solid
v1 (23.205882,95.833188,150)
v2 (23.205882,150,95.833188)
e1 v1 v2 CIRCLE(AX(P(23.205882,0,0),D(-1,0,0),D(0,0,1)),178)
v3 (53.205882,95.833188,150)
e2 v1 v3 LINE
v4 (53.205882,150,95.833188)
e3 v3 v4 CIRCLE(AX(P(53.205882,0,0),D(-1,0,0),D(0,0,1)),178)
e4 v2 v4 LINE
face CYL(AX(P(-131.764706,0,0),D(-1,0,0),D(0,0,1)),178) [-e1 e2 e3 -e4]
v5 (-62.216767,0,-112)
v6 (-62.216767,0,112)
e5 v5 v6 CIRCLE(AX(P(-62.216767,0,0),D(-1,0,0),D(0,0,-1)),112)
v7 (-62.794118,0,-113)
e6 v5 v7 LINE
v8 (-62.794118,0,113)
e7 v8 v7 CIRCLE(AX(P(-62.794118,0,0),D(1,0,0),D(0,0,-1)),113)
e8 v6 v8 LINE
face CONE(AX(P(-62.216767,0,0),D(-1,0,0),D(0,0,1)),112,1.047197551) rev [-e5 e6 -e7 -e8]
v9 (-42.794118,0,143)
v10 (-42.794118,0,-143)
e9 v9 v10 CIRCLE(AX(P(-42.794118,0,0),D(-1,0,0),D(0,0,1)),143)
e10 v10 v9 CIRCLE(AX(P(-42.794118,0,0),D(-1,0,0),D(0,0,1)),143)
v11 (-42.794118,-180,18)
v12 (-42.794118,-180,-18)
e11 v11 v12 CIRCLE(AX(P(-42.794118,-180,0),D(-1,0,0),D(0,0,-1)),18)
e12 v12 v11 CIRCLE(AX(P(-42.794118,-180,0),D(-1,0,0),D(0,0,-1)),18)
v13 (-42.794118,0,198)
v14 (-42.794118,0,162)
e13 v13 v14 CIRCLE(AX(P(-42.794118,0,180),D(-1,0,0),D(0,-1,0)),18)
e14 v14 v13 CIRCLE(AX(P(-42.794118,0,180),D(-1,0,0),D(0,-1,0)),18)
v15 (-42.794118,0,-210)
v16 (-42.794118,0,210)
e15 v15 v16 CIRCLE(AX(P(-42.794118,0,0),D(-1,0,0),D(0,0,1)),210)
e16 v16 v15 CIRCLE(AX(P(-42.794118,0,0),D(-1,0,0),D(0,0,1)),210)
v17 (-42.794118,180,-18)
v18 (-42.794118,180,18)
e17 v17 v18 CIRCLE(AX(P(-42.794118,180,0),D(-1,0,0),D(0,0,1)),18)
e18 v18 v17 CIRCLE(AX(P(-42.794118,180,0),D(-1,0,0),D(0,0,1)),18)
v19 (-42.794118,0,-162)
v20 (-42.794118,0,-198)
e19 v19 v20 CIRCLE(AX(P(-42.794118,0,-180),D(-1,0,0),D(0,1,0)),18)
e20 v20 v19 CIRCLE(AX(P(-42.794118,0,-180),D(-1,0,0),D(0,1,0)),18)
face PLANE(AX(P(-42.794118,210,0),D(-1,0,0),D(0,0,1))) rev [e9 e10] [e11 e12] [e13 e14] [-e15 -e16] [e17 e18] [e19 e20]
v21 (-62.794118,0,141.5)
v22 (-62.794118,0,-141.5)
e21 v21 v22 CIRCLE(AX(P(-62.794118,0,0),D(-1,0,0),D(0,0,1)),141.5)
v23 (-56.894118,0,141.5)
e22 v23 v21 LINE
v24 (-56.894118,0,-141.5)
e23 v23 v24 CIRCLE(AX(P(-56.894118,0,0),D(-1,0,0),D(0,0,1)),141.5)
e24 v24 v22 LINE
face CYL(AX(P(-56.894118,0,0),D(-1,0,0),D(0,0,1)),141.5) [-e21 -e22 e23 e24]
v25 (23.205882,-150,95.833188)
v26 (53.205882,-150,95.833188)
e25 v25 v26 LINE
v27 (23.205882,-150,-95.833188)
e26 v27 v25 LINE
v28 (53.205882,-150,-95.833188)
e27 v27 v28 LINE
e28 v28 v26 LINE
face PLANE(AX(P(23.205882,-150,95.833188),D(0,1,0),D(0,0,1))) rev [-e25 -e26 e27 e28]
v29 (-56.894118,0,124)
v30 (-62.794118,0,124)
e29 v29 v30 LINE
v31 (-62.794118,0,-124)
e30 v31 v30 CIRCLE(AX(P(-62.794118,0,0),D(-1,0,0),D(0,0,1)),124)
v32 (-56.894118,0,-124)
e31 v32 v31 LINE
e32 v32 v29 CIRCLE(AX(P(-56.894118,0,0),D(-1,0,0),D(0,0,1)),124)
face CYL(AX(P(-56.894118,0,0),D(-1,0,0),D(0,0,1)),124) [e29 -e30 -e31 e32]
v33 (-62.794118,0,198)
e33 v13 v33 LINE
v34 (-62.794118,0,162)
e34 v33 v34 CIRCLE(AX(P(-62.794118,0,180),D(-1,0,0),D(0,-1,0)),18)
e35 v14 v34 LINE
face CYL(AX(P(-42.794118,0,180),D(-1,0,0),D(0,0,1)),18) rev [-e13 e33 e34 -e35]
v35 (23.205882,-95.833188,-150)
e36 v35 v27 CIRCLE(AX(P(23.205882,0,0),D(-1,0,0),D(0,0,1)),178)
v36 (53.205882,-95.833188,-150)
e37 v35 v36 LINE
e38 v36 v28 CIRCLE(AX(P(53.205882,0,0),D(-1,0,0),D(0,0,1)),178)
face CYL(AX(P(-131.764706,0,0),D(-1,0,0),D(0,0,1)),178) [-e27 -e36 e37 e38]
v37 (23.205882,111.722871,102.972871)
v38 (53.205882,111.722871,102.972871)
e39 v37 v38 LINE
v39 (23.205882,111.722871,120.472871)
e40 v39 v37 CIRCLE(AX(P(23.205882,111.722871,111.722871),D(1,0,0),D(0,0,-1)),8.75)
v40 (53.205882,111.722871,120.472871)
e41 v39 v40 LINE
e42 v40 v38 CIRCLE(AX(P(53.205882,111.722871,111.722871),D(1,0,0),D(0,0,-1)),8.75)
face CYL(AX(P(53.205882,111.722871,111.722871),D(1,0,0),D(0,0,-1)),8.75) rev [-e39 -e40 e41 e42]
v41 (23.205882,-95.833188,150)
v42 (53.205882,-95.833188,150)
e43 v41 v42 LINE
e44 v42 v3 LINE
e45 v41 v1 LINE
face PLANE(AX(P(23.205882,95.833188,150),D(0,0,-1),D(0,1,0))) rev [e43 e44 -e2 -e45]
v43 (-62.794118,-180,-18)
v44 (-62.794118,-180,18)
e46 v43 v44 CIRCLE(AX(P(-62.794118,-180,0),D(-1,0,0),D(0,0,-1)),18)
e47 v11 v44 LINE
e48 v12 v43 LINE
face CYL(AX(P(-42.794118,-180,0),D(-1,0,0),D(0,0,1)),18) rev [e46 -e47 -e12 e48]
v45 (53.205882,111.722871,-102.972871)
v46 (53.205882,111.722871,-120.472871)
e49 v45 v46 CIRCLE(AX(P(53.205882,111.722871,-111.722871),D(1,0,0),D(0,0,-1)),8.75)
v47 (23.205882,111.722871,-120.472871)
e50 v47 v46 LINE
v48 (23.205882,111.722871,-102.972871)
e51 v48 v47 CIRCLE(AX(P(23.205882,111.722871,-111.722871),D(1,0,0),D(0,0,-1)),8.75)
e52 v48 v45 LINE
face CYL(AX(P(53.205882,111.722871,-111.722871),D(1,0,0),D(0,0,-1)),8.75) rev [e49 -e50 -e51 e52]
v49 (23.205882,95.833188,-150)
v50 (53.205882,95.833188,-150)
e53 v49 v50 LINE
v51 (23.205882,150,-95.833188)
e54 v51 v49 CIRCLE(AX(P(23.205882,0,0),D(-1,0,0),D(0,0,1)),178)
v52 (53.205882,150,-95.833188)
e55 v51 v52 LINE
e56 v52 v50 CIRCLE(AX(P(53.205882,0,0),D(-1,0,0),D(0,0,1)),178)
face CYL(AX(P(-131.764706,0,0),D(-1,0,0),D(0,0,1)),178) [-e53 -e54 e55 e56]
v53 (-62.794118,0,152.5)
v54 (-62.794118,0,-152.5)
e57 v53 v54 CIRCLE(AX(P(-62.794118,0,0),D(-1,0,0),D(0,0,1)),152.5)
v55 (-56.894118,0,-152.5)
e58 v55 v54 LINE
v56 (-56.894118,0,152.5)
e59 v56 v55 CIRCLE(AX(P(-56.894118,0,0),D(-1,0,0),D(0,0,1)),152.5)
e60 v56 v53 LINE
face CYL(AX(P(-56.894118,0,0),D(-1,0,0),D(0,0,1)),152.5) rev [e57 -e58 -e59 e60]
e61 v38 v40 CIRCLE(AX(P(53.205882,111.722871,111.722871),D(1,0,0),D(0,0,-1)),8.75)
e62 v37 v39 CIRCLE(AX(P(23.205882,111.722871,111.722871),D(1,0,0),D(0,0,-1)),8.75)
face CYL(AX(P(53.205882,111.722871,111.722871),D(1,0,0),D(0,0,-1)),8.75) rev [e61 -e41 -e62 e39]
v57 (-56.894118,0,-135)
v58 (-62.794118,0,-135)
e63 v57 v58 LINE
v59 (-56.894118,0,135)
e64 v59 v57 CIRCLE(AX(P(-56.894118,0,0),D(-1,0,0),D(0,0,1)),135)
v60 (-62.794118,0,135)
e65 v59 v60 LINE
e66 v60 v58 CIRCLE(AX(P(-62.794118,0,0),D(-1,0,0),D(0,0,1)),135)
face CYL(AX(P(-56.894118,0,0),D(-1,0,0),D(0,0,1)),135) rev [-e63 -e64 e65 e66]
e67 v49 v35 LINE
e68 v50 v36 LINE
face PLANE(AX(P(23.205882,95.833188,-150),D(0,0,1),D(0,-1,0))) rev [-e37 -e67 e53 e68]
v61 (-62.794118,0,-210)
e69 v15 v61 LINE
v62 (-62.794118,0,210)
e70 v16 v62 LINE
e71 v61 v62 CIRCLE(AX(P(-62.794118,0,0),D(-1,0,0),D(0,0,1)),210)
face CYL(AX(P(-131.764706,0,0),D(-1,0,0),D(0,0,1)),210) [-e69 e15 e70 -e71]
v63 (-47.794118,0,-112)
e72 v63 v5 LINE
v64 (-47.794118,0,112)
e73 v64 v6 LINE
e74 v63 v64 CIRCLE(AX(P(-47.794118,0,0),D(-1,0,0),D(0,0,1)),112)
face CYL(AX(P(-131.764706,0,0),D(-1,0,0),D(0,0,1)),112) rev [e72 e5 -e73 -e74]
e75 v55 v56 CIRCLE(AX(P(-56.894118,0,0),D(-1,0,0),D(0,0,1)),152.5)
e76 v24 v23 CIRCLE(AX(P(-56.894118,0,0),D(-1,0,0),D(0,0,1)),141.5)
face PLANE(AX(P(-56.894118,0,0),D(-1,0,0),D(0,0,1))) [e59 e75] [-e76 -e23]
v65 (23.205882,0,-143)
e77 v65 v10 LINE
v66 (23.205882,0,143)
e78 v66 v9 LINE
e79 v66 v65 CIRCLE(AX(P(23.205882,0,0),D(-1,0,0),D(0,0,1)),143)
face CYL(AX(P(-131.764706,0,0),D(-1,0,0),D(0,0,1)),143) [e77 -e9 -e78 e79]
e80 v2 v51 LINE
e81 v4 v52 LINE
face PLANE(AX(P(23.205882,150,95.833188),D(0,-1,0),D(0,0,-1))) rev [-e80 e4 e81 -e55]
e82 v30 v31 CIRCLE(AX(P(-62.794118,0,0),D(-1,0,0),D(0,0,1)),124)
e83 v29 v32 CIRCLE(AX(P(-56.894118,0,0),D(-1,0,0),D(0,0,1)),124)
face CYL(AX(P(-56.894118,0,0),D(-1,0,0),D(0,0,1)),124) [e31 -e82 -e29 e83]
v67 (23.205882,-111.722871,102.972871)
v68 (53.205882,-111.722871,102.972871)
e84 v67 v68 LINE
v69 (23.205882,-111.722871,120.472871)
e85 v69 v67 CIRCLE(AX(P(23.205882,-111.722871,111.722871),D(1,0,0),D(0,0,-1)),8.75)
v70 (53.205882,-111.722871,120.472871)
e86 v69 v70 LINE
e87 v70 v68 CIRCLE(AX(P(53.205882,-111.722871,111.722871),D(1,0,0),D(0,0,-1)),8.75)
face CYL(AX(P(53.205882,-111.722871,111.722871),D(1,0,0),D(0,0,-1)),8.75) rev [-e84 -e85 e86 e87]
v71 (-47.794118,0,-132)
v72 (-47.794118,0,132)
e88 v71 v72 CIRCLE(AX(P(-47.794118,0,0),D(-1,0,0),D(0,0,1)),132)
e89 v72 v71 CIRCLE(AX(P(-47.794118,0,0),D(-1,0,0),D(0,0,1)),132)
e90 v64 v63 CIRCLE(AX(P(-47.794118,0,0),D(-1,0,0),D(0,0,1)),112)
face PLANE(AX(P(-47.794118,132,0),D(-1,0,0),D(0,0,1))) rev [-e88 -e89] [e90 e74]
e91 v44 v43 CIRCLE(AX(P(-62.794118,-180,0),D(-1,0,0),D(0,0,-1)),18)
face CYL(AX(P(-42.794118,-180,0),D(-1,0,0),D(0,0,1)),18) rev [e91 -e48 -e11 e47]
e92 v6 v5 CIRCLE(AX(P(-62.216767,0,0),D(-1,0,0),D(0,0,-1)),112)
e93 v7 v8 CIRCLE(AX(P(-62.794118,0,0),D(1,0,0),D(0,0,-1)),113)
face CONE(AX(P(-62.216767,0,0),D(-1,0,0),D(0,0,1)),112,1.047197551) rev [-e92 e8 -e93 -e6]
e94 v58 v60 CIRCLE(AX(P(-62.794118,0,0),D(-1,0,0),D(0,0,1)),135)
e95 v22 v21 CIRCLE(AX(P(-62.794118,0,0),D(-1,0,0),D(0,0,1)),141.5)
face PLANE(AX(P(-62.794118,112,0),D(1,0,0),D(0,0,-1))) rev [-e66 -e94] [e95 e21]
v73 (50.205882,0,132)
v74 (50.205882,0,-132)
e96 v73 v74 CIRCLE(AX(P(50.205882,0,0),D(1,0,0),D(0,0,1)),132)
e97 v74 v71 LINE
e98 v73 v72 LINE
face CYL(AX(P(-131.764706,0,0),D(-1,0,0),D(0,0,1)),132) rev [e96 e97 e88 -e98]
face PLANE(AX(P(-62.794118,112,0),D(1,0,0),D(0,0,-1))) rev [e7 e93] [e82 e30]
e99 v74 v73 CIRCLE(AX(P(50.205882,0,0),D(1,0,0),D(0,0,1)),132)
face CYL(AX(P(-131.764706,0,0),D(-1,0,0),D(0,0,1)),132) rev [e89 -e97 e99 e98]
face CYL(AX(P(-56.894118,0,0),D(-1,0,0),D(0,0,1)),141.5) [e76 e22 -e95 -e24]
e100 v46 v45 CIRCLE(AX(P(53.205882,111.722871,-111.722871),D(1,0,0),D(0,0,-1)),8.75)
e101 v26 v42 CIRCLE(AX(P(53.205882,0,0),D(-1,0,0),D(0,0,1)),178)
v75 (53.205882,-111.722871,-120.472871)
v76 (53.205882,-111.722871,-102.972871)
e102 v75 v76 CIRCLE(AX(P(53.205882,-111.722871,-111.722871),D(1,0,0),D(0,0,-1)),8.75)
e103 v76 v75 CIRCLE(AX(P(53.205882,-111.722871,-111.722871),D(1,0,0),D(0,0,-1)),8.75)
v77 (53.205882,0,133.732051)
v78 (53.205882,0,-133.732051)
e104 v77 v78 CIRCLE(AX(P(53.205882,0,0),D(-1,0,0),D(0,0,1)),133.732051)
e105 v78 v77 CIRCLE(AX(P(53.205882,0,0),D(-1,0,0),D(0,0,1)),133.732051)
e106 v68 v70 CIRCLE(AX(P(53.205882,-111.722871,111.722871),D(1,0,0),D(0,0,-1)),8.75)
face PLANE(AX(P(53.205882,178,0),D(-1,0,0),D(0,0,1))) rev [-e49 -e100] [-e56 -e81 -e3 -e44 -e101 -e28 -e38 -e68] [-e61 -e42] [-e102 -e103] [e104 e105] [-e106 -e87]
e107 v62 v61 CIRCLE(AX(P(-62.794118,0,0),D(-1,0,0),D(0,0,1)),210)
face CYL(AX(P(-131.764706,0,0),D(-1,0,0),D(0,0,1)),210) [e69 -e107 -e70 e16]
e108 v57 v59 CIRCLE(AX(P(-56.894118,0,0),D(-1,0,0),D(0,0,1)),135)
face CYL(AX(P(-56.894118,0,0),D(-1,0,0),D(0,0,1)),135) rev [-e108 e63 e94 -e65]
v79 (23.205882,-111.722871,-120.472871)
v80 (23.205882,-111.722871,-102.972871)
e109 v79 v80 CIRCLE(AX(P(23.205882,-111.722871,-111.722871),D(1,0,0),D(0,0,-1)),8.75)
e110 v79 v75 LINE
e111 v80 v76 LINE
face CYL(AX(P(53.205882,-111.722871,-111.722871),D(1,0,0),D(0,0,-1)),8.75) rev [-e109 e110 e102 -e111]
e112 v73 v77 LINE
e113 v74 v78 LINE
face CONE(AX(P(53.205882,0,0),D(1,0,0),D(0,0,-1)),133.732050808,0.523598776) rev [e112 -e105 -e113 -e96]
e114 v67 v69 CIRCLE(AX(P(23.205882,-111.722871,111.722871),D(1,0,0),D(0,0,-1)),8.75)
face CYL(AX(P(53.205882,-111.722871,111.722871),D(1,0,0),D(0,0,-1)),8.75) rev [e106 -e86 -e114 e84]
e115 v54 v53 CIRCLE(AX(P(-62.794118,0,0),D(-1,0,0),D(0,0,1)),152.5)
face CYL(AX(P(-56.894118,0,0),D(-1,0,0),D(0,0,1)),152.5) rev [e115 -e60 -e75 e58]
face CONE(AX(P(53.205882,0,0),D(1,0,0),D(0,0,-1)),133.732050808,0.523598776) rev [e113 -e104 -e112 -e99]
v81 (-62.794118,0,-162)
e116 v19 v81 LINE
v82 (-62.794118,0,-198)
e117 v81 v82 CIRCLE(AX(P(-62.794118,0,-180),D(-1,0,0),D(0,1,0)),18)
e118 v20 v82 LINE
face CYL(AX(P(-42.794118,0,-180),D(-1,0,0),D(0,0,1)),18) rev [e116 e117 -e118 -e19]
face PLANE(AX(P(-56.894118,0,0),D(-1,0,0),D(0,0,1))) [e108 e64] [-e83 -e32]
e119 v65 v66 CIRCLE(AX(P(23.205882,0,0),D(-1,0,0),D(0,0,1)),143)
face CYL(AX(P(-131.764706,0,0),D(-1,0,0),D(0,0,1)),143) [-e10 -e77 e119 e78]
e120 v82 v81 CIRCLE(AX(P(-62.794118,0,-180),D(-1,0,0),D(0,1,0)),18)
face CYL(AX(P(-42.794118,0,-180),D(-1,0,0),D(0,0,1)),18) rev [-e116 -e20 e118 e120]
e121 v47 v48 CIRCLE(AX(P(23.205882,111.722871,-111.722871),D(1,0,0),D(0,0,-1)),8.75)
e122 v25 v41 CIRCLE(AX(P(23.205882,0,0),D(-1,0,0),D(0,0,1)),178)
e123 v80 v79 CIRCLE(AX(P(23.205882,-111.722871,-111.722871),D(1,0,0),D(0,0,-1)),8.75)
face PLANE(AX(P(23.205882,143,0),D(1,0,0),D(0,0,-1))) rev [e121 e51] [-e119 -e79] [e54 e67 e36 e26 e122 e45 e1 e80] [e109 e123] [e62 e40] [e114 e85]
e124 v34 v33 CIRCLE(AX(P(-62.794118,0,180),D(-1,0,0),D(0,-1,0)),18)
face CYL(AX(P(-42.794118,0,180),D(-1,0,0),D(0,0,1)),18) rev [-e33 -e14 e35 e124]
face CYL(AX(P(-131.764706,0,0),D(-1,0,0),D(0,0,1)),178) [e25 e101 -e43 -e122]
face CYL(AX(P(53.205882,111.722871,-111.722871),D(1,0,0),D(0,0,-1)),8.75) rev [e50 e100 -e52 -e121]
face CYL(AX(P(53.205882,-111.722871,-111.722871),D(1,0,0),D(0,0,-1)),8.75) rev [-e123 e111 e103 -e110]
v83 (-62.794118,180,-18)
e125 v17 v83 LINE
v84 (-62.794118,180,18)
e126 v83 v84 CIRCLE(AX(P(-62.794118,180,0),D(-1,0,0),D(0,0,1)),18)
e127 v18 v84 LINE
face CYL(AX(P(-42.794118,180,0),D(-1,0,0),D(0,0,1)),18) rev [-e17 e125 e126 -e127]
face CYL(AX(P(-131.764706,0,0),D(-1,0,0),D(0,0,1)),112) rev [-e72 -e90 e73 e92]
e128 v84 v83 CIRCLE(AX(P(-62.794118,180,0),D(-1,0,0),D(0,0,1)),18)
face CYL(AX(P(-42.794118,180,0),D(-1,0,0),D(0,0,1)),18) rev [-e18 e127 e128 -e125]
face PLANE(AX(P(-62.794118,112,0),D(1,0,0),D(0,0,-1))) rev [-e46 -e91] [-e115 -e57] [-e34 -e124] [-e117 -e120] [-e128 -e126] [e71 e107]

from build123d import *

# Parameters (mm, degrees)
SKETCH5_R          = 152.5
SKETCH5_R_2        = 141.5
CUT_EXTRUDE1_DEPTH = 5.9
SKETCH6_R          = 135
SKETCH6_R_2        = 124
CUT_EXTRUDE2_DEPTH = 5.9
SKETCH7_R          = 18
CUT_EXTRUDE3_DEPTH = 20
CIRPATTERN1_COUNT  = 4
CIRPATTERN2_COUNT  = 4
CUT_EXTRUDE4_DEPTH = 30
CHAMFER1_SIZE      = 3
CHAMFER1_SIZE2     = 1.732050808
CHAMFER2_SIZE      = 1
CHAMFER2_SIZE2     = 0.577350269


with BuildPart() as part:
    # Sketch4 → Revolve1 (revolve)
    with BuildSketch(Plane.XY, mode=Mode.PRIVATE) as revolve1_sk:
        Polygon((-62.794117647, 112), (-62.794117647, 210), (-42.794117647, 210), (-42.794117647, 143), (23.205882353, 143), (23.205882353, 178), (53.205882353, 178), (53.205882353, 132), (-47.794117647, 132), (-47.794117647, 112), align=None)
    revolve(revolve1_sk.sketch.rotate(Axis((-131.764705882, 0, 0), (1, 0, 0)), 90), axis=Axis((-131.764705882, 0, 0), (1, 0, 0)))

    # Sketch5 → Cut-Extrude1 (cut)
    with BuildSketch(Plane.ZY.offset(62.794117647)):
        Circle(SKETCH5_R)
        Circle(SKETCH5_R_2, mode=Mode.SUBTRACT)
    extrude(amount=-CUT_EXTRUDE1_DEPTH, mode=Mode.SUBTRACT)

    # Sketch6 → Cut-Extrude2 (cut)
    with BuildSketch(Plane.ZY.offset(62.794117647)):
        Circle(SKETCH6_R)
        Circle(SKETCH6_R_2, mode=Mode.SUBTRACT)
    extrude(amount=-CUT_EXTRUDE2_DEPTH, mode=Mode.SUBTRACT)

    # Sketch7 → Cut-Extrude3 (cut)
    with BuildSketch(Plane.ZY.offset(62.794117647)):
        with Locations((0, 180)):
            Circle(SKETCH7_R)
    cut_extrude3 = extrude(amount=-CUT_EXTRUDE3_DEPTH, mode=Mode.SUBTRACT)

    # CirPattern1: Cut-Extrude3 ×4 about axis
    cirpattern1_axis = Axis((0, 0, 0), (1, 0, 0))
    for i in range(1, CIRPATTERN1_COUNT):
        add(cut_extrude3.rotate(cirpattern1_axis, i * 360 / CIRPATTERN1_COUNT), mode=Mode.SUBTRACT)

    # Sketch9 → M20 Tapped Hole1 (revolve, cut)
    with BuildSketch(Plane(origin=(53.205882353, 111.722871427, -111.722871427), x_dir=(0, 0, -1), z_dir=(0, 1, 0))):
        Polygon((0, 0), (0, 57.757530416), (8.75, 52.5), (8.75, 0), align=None)
    m20_tapped_hole1 = revolve(axis=Axis((59.555882353, 111.722871427, -111.722871427), (-1, 0, 0)), mode=Mode.SUBTRACT)

    # CirPattern2: M20 Tapped Hole1 ×4 about axis
    cirpattern2_axis = Axis((0, 0, 0), (1, 0, 0))
    for i in range(1, CIRPATTERN2_COUNT):
        add(m20_tapped_hole1.rotate(cirpattern2_axis, i * 360 / CIRPATTERN2_COUNT), mode=Mode.SUBTRACT)

    # Sketch12 → Cut-Extrude4 (cut)
    with BuildSketch(Plane(origin=(53.205882353, 0, 0), x_dir=(0, 0, -1), z_dir=(1, 0, 0))):
        with BuildLine():
            Line((-95.833188406, 150), (95.833188406, 150))
            ThreePointArc((95.833188406, 150), (0, 178), (-95.833188406, 150))
        make_face()
        with BuildLine():
            Line((-150, 95.833188406), (-150, -95.833188406))
            ThreePointArc((-150, -95.833188406), (-178, 0), (-150, 95.833188406))
        make_face()
        with BuildLine():
            Line((-95.833188406, -150), (95.833188406, -150))
            ThreePointArc((95.833188406, -150), (0, -178), (-95.833188406, -150))
        make_face()
        with BuildLine():
            Line((150, 95.833188406), (150, -95.833188406))
            ThreePointArc((150, -95.833188406), (178, 0), (150, 95.833188406))
        make_face()
    extrude(amount=-CUT_EXTRUDE4_DEPTH, mode=Mode.SUBTRACT)

    # Chamfer1
    chamfer1_edges = [part.edges().sort_by_distance(p)[0] for p in [
        (53.205882353, 0, -132),
    ]]
    chamfer1_side = [part.faces().sort_by_distance(p)[0] for p in [
        (2.705882353, 0, -132),
    ]]
    chamfer(chamfer1_edges, length=CHAMFER1_SIZE, length2=CHAMFER1_SIZE2, reference=chamfer1_side[0])

    # Chamfer2
    chamfer2_edges = [part.edges().sort_by_distance(p)[0] for p in [
        (-62.794117647, 0, -112),
    ]]
    chamfer2_side = [part.faces().sort_by_distance(p)[0] for p in [
        (-62.794117647, 0, -120.492750365),
    ]]
    chamfer(chamfer2_edges, length=CHAMFER2_SIZE, length2=CHAMFER2_SIZE2, reference=chamfer2_side[0])


solid = part.part
